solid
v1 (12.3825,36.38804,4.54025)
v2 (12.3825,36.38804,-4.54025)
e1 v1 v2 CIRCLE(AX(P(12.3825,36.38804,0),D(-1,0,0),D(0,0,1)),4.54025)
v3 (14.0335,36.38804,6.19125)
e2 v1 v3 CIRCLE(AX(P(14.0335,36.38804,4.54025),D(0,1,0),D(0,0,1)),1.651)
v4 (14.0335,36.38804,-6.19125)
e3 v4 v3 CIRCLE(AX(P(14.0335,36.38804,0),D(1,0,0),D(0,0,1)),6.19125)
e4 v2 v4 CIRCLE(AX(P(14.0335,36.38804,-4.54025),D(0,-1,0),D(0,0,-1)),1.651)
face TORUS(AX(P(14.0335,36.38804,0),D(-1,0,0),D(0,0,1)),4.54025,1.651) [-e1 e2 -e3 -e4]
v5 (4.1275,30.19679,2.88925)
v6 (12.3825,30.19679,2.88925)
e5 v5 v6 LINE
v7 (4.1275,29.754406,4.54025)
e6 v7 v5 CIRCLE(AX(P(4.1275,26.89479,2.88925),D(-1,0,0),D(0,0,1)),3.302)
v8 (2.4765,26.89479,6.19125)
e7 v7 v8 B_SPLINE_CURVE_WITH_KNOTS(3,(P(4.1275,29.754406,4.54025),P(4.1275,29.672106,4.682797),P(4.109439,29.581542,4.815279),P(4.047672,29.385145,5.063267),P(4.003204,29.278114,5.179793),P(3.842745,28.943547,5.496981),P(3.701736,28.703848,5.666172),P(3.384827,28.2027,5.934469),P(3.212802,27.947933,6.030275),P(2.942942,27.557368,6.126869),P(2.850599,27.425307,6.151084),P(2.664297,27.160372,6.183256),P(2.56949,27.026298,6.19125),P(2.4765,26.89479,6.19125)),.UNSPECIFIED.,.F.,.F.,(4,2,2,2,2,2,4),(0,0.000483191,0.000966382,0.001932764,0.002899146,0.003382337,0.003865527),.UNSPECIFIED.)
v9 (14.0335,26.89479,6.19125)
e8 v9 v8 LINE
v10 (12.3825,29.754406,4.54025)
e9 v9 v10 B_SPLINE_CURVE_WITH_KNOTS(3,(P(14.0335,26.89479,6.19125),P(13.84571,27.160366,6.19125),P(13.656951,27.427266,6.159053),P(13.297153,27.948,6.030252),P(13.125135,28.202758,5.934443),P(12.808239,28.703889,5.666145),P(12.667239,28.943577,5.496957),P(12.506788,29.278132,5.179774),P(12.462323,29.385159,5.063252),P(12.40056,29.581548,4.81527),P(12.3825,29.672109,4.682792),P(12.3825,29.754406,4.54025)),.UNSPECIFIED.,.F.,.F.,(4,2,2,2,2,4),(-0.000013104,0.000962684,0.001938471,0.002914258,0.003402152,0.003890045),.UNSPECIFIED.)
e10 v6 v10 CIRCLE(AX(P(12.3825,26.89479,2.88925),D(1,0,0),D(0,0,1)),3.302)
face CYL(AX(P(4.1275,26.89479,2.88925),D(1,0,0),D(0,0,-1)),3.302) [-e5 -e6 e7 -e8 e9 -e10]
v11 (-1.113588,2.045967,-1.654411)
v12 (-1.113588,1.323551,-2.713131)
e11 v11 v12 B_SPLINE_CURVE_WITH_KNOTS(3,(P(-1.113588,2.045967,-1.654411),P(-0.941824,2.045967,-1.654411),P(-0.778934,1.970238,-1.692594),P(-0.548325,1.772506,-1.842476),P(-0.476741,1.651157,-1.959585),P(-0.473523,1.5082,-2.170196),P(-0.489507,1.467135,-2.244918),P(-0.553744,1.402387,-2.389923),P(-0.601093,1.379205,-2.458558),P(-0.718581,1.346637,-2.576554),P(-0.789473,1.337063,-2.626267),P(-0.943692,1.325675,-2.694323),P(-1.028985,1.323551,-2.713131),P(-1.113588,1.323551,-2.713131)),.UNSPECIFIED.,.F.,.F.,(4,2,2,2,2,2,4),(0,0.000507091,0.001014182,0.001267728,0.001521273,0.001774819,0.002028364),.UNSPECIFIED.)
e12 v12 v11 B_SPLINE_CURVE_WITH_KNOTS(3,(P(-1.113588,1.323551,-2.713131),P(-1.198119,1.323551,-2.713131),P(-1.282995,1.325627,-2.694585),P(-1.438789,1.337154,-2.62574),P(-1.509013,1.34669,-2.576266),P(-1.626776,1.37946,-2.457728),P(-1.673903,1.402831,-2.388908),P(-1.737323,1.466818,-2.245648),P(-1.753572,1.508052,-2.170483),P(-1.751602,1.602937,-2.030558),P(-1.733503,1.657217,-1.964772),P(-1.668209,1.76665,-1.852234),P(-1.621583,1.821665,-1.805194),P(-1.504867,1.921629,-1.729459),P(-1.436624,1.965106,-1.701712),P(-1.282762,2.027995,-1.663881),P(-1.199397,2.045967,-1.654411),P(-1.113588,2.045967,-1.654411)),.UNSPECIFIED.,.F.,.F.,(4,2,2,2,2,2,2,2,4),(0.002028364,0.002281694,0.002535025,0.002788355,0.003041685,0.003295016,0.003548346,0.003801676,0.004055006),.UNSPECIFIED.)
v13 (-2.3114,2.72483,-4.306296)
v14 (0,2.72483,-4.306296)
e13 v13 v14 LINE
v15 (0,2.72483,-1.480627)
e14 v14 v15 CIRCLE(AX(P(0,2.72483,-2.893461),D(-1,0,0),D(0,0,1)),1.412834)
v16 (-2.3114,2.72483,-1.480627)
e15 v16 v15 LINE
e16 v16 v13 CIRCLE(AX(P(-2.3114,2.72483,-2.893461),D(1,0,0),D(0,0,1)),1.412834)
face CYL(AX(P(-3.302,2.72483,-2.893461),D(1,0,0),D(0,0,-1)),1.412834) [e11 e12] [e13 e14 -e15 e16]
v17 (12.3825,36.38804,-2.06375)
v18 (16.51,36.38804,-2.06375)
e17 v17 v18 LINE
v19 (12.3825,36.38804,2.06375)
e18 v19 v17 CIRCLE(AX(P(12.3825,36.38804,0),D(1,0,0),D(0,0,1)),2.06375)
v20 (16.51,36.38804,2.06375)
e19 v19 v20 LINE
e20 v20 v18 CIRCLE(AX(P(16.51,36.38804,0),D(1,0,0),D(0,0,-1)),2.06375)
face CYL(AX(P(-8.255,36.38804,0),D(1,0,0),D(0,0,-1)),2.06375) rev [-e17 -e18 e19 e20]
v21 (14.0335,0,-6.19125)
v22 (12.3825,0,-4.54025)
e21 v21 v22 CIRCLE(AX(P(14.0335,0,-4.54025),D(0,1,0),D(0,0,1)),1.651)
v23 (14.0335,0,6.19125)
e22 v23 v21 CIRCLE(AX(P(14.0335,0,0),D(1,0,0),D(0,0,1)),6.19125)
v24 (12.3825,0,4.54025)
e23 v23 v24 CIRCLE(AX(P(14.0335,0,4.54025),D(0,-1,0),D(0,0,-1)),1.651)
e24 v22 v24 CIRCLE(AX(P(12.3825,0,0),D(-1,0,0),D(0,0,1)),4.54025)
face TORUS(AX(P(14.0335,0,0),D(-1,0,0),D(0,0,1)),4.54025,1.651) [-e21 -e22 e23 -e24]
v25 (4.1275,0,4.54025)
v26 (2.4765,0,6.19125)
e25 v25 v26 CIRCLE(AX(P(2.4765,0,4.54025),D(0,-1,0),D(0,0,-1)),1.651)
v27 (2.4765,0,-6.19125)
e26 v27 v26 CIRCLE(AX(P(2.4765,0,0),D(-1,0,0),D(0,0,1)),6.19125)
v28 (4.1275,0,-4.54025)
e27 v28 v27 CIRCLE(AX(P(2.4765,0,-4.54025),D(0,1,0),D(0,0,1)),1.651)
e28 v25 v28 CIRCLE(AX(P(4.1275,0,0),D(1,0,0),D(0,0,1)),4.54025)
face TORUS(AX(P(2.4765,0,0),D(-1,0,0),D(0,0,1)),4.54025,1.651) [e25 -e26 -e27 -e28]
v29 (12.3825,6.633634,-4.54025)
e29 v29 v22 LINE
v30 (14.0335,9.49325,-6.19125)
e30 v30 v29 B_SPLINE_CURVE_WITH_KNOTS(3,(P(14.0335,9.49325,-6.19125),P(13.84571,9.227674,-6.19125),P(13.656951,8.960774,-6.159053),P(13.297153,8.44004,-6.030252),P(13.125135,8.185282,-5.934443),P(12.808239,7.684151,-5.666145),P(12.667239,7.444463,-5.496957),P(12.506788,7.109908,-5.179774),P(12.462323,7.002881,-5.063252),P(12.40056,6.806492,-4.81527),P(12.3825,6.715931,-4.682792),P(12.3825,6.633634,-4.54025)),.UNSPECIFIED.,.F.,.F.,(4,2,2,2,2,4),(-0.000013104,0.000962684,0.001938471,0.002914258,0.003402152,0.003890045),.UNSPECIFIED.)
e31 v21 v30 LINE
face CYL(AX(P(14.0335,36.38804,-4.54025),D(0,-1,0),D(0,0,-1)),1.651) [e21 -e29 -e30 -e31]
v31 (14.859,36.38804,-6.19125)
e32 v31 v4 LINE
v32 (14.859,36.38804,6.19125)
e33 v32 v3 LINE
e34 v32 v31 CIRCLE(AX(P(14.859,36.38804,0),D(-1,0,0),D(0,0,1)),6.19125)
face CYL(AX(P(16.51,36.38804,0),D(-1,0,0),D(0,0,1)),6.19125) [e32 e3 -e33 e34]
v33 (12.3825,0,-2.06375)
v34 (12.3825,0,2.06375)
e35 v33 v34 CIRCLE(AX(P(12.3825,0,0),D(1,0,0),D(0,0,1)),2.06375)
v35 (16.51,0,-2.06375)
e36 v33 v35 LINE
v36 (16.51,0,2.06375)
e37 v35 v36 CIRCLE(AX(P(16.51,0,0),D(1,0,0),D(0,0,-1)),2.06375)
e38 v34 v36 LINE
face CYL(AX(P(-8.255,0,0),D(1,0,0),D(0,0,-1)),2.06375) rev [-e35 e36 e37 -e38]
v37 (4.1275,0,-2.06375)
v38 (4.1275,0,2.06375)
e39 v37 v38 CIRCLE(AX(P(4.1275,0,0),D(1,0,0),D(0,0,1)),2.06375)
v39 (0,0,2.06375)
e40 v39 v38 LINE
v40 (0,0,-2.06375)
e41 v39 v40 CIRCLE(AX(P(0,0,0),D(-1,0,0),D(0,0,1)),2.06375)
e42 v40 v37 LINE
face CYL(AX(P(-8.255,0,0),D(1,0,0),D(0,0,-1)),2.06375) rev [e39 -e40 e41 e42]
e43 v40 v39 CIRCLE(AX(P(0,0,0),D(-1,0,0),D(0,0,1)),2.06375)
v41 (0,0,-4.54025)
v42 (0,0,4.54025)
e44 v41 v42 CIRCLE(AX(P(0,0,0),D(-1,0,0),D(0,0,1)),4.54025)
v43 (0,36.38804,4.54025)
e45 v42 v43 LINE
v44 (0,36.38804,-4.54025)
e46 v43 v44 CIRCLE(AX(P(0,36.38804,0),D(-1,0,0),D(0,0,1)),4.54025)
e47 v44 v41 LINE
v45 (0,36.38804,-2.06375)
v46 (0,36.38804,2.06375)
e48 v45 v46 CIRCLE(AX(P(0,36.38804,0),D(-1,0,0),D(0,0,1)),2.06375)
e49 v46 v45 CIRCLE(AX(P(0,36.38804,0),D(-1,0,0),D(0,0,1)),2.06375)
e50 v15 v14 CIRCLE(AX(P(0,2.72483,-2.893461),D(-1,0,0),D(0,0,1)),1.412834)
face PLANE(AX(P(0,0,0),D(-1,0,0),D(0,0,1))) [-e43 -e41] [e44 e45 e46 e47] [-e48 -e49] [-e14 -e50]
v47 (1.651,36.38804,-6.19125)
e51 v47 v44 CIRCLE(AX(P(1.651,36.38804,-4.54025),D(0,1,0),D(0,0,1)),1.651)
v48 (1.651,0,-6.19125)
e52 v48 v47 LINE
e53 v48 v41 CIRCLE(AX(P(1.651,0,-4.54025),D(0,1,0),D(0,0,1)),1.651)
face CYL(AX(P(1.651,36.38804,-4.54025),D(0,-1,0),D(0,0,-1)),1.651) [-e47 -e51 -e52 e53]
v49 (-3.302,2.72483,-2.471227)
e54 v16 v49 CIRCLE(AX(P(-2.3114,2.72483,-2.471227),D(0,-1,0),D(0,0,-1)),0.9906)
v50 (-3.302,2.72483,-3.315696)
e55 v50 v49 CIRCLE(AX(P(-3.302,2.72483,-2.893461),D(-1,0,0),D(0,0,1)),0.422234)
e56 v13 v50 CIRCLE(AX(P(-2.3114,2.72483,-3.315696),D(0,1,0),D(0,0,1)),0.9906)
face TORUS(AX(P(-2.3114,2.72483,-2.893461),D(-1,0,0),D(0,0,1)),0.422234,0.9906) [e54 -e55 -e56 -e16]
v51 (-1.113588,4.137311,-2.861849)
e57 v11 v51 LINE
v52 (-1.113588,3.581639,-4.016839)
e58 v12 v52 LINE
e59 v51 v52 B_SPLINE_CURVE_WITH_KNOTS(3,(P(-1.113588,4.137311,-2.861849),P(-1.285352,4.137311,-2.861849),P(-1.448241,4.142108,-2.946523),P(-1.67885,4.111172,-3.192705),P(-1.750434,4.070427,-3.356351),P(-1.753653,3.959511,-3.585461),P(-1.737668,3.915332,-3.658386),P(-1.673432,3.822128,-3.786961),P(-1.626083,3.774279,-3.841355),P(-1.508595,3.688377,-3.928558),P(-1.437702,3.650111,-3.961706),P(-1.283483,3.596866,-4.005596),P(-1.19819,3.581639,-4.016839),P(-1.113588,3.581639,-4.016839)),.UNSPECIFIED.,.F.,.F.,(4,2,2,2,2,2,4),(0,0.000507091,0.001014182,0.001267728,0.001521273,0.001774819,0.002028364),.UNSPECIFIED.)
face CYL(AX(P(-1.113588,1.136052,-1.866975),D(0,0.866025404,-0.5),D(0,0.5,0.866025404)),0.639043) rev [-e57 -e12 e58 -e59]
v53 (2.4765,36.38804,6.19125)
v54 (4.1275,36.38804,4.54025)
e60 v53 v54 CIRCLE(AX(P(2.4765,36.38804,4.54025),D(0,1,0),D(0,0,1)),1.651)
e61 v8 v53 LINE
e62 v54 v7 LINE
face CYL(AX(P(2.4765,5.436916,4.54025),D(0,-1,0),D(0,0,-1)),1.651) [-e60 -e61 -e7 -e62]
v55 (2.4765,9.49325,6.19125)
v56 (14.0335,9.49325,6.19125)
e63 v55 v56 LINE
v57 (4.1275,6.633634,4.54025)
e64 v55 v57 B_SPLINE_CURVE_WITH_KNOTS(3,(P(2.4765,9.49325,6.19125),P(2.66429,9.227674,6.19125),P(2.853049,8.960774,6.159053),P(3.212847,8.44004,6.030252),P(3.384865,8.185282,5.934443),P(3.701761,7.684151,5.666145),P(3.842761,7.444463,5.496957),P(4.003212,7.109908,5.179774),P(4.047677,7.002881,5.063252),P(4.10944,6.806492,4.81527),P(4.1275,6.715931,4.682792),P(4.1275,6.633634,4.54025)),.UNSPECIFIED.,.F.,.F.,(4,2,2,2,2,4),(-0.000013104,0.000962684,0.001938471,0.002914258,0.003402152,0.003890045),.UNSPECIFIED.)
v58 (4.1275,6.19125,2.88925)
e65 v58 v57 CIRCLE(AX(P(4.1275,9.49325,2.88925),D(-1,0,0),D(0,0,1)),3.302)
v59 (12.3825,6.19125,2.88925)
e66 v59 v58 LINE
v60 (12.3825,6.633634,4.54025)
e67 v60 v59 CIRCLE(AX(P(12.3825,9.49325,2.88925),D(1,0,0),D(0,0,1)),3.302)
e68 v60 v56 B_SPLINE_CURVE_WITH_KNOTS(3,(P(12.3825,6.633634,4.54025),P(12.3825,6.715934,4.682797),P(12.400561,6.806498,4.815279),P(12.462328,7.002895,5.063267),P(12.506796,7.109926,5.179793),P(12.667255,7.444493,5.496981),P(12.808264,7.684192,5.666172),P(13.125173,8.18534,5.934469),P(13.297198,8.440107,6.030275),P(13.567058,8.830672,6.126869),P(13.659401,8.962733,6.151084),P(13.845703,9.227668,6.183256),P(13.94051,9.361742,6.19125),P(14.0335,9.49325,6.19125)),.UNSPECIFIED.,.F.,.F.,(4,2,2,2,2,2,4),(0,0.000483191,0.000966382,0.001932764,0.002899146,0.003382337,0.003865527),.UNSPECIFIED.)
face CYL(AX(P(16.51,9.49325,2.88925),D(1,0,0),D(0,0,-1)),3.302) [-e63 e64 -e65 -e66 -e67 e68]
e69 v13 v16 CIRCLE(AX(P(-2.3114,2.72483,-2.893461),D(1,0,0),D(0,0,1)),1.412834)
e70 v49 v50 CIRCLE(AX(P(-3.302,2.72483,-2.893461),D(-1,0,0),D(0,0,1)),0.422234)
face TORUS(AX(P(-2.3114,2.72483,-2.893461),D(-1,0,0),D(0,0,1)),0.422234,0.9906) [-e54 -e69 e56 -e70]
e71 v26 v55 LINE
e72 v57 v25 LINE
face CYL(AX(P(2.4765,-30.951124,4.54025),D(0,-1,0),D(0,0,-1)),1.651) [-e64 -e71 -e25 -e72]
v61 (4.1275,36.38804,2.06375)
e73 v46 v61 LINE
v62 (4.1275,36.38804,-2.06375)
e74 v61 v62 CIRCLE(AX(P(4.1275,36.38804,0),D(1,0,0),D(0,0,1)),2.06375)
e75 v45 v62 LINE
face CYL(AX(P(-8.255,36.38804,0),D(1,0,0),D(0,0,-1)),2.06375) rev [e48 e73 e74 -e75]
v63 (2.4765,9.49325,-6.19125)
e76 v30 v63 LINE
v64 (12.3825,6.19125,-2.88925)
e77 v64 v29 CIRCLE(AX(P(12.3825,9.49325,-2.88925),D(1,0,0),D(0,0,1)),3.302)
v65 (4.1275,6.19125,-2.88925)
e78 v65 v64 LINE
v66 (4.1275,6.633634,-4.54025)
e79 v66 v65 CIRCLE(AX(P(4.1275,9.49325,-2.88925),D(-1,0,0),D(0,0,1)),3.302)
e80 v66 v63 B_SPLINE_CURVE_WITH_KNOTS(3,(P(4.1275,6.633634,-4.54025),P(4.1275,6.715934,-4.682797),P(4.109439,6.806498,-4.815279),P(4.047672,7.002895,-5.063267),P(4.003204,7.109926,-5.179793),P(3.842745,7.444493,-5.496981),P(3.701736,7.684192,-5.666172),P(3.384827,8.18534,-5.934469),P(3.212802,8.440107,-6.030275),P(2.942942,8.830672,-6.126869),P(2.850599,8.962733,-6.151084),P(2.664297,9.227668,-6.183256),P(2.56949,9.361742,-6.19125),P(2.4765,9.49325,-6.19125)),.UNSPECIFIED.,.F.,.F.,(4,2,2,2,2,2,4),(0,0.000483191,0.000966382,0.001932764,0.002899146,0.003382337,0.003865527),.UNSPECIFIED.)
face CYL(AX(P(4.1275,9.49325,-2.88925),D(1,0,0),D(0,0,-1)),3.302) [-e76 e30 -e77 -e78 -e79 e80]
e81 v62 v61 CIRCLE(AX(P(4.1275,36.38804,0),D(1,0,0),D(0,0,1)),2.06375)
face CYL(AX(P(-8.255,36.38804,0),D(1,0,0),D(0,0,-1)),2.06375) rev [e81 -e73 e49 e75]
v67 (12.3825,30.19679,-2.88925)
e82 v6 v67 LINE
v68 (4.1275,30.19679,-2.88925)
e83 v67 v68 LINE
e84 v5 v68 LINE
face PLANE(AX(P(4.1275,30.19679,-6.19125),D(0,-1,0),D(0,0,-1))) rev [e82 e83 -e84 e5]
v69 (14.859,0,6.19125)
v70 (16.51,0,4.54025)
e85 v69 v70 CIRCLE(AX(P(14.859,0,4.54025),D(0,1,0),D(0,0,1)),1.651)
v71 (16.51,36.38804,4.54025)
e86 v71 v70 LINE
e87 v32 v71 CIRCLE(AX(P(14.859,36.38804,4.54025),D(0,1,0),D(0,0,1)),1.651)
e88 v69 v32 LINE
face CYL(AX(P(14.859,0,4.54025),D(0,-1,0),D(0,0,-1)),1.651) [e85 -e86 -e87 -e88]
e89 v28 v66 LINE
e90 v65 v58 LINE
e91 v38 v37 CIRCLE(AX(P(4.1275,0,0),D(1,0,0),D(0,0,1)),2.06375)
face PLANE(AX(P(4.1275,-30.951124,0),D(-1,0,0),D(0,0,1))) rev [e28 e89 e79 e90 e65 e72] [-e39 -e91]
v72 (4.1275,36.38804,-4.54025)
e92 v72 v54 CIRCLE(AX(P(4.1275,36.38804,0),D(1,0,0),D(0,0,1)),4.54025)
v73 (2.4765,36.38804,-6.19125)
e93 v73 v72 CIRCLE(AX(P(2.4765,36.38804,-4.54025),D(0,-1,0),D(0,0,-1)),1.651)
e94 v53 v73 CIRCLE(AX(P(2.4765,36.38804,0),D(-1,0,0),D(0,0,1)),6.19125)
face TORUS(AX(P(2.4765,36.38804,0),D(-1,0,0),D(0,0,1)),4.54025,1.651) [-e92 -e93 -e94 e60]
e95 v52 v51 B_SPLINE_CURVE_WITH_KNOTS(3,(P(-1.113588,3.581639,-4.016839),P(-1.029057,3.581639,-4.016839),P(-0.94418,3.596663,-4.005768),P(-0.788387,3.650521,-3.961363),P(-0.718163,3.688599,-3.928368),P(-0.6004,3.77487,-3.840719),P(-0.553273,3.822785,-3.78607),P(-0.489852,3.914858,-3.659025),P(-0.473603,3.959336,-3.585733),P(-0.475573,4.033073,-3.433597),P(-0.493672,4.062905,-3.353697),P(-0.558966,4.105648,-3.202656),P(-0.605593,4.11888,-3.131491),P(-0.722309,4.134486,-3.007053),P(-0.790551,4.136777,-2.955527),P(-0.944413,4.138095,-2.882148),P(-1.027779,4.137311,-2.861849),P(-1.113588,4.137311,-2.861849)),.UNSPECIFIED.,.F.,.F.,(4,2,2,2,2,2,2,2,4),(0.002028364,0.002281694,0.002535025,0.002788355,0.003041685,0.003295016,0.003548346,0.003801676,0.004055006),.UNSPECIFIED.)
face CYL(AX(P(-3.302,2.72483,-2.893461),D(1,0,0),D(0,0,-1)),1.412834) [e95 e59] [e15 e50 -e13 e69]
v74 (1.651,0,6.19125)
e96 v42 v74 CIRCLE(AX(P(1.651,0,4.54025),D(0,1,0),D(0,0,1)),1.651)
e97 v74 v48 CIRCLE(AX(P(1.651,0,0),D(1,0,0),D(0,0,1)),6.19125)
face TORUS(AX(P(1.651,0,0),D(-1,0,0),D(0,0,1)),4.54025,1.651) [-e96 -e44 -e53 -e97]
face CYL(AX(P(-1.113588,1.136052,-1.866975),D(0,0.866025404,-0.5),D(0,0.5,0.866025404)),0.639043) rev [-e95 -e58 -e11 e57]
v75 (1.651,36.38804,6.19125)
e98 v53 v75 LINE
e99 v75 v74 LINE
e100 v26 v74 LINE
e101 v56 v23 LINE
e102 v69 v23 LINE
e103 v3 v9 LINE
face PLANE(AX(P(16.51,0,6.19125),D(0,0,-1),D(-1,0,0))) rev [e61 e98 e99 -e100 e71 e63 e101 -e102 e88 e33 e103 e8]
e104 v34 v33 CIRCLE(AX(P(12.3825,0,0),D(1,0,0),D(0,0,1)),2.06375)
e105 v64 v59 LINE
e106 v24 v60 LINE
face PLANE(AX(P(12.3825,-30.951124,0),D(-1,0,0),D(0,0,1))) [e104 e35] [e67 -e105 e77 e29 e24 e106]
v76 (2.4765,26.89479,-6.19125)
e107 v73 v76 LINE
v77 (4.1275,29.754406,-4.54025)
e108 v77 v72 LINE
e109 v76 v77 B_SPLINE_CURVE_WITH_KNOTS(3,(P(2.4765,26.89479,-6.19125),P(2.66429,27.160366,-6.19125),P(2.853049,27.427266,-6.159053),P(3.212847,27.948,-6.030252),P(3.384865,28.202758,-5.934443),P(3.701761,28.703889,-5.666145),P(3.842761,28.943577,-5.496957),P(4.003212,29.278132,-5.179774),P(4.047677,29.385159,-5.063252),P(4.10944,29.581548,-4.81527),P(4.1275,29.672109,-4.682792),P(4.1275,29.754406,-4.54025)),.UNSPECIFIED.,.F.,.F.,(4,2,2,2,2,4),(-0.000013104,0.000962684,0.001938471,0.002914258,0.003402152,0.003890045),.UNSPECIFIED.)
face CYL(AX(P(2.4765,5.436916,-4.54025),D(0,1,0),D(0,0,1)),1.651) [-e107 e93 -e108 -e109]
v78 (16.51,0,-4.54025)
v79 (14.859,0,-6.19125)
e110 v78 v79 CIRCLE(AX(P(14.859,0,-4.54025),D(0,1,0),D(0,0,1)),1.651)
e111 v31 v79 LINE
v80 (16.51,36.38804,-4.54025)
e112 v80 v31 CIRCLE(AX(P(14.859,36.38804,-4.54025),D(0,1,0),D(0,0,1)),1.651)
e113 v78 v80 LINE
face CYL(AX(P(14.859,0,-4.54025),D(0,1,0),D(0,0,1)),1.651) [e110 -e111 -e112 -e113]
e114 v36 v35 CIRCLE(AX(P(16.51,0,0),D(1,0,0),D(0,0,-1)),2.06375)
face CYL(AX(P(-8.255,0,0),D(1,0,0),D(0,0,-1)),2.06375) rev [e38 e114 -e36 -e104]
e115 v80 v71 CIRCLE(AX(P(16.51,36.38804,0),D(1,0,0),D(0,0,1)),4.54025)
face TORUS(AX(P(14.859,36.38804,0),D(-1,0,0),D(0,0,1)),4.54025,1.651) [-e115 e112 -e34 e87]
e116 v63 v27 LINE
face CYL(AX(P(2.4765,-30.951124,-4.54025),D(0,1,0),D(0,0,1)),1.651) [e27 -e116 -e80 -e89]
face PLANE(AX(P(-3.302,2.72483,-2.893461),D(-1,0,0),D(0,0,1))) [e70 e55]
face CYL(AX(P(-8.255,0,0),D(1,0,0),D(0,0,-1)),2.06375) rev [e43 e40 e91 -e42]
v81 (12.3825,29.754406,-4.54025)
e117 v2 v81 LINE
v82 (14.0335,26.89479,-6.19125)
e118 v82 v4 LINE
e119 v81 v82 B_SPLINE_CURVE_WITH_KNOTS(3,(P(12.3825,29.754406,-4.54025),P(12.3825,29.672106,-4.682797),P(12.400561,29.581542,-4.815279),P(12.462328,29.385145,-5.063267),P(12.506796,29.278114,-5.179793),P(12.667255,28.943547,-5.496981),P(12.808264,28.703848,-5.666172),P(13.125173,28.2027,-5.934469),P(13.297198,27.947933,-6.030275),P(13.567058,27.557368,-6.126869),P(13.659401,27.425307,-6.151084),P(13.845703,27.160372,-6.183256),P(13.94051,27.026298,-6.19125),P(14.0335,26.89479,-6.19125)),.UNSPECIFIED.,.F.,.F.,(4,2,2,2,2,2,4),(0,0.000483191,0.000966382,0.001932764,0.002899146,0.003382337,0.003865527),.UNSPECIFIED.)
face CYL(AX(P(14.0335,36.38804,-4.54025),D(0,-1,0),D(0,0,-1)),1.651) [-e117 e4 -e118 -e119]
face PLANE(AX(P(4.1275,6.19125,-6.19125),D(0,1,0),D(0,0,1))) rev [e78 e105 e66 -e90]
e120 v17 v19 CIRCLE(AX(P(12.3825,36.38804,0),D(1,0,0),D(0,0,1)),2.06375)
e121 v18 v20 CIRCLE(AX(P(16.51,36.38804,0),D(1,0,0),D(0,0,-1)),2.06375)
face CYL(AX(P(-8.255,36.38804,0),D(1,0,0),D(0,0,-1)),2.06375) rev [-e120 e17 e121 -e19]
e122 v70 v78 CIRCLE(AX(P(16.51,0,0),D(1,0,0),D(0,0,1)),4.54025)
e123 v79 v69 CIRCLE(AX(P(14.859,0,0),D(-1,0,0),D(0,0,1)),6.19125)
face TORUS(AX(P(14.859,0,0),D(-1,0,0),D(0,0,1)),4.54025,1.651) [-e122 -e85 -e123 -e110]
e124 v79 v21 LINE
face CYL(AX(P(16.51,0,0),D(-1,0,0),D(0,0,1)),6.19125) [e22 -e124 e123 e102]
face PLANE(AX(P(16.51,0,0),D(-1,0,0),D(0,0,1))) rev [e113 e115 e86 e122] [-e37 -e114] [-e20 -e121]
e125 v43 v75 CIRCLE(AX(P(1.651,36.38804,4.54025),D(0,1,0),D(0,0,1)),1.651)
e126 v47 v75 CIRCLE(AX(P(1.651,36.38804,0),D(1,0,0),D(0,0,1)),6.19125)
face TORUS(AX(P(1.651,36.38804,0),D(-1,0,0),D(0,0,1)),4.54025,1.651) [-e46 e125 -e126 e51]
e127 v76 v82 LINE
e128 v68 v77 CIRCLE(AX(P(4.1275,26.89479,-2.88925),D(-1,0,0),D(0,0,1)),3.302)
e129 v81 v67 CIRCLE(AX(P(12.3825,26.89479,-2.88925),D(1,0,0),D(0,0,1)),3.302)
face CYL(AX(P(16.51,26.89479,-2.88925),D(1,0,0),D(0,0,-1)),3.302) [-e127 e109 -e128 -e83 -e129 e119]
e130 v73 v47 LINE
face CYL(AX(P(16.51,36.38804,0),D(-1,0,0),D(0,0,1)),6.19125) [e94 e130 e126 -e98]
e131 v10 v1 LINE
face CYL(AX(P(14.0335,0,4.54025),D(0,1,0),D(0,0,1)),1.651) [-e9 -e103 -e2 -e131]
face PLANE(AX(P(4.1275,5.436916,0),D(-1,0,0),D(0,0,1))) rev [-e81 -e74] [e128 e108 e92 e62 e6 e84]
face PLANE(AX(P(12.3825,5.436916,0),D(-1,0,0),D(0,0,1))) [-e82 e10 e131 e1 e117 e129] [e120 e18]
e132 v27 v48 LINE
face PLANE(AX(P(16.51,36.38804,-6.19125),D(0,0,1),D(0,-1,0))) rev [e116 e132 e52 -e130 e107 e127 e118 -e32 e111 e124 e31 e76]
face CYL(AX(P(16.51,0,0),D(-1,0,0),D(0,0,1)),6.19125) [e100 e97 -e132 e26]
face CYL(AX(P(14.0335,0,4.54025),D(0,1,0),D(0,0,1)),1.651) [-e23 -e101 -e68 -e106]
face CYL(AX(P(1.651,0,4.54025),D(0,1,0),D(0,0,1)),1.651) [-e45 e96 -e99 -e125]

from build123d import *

# Parameters (mm, degrees)
BOSS_EXTRUDE1_DEPTH = 12.7
SKETCH2_R           = 1.5875
CUT_EXTRUDE1_DEPTH  = 19.05
CUT_EXTRUDE2_DEPTH  = 3.175
FILLET2_R           = 2.54
FILLET3_R           = 1.27
SKETCH3_R           = 1.086795662
BOSS_EXTRUDE2_DEPTH = 2.54
FILLET4_R           = 0.762
SKETCH4_R           = 0.491571792
CUT_EXTRUDE3_DEPTH  = 2.54
SCALE_RATIO_1_SCALE = 1.3


with BuildPart() as part:
    # Sketch1 → Boss-Extrude1 (new body)
    with BuildSketch(Plane(origin=(0, 0, 0), x_dir=(0, 0, -1), z_dir=(1, 0, 0))):
        with BuildLine():
            Line((-4.7625, 0), (-4.7625, 27.9908))
            ThreePointArc((-4.7625, 27.9908), (0, 32.7533), (4.7625, 27.9908))
            Line((4.7625, 27.9908), (4.7625, 0))
            ThreePointArc((4.7625, 0), (0, -4.7625), (-4.7625, 0))
        make_face()
    extrude(amount=BOSS_EXTRUDE1_DEPTH)

    # Sketch2 → Cut-Extrude1 (cut)
    with BuildSketch(Plane(origin=(12.7, 0, 0), x_dir=(0, 0, -1), z_dir=(1, 0, 0))):
        Circle(SKETCH2_R)
        with Locations((0, 27.9908)):
            Circle(SKETCH2_R)
    extrude(amount=-CUT_EXTRUDE1_DEPTH, mode=Mode.SUBTRACT)

    # 3DSketch1 → Cut-Extrude2 (cut, symmetric)
    with BuildSketch(Plane(origin=(6.35, 27.9908, -4.7625), x_dir=(0, -0.9466889316456175, 0.322149137356721), z_dir=(1, 0, 0))):
        with BuildLine():
            Line((0, 0), (4.508606037, 1.534235267))
            Line((4.508606037, 1.534235267), (7.57707657, -7.482976807))
            Line((7.57707657, -7.482976807), (3.068470533, -9.017212074))
            ThreePointArc((3.068470533, -9.017212074), (-2.97437077, -6.042841304), (0, 0))
        make_face()
        with BuildLine():
            Line((29.567051081, 0), (25.058445044, -1.534235267))
            Line((25.058445044, -1.534235267), (21.989974511, 7.482976807))
            Line((21.989974511, 7.482976807), (26.498580548, 9.017212074))
            ThreePointArc((26.498580548, 9.017212074), (32.541421852, 6.042841304), (29.567051081, 0))
        make_face()
    extrude(amount=CUT_EXTRUDE2_DEPTH, both=True, mode=Mode.SUBTRACT)

    # Fillet2
    fillet2_edges = [part.edges().sort_by_distance(p)[0] for p in [
        (6.35, 23.2283, -4.7625),
        (6.35, 4.7625, -4.7625),
        (6.35, 4.7625, 4.7625),
        (6.35, 23.2283, 4.7625),
    ]]
    fillet(fillet2_edges, radius=FILLET2_R)

    # Fillet3
    fillet3_edges = [part.edges().sort_by_distance(p)[0] for p in [
        (12.7, 32.7533, 0),
        (12.7, 13.9954, 4.7625),
        (9.525, 24.33955, 4.7625),
        (9.525, 24.33955, -4.7625),
        (3.175, 24.33955, -4.7625),
        (3.175, 24.33955, 4.7625),
        (12.7, -4.7625, 0),
        (0, 13.9954, 4.7625),
        (0, 32.7533, 0),
        (9.525, 3.65125, -4.7625),
        (9.525, 3.65125, 4.7625),
        (0, 13.9954, -4.7625),
        (3.175, 3.65125, 4.7625),
        (3.175, 3.65125, -4.7625),
        (0, -4.7625, 0),
        (12.7, 13.9954, -4.7625),
    ]]
    fillet(fillet3_edges, radius=FILLET3_R)

    # Sketch3 → Boss-Extrude2 (add)
    with BuildSketch(Plane.ZY):
        with Locations((-2.225739377, 2.096022994)):
            Circle(SKETCH3_R)
    extrude(amount=BOSS_EXTRUDE2_DEPTH)

    # Fillet4
    fillet4_edges = [part.edges().sort_by_distance(p)[0] for p in [
        (-2.54, 2.096022994, -3.312535039),
    ]]
    fillet(fillet4_edges, radius=FILLET4_R)

    # Sketch4 → Cut-Extrude3 (cut)
    with BuildSketch(Plane(origin=(0, 3.476983319, -2.007437255), x_dir=(-1, 0, 0), z_dir=(0, 0.8660254037844399, -0.4999999999999979))):
        with Locations(Location((0.856605906, -0.806785971, 0), (0, 0, 90))):
            Circle(SKETCH4_R)
    extrude(amount=-CUT_EXTRUDE3_DEPTH, mode=Mode.SUBTRACT)


with BuildPart() as part_1:
    # Scale ratio 1: scaled about (0, 0, 0)
    add(part.part.scale(SCALE_RATIO_1_SCALE))


solid = part_1.part
